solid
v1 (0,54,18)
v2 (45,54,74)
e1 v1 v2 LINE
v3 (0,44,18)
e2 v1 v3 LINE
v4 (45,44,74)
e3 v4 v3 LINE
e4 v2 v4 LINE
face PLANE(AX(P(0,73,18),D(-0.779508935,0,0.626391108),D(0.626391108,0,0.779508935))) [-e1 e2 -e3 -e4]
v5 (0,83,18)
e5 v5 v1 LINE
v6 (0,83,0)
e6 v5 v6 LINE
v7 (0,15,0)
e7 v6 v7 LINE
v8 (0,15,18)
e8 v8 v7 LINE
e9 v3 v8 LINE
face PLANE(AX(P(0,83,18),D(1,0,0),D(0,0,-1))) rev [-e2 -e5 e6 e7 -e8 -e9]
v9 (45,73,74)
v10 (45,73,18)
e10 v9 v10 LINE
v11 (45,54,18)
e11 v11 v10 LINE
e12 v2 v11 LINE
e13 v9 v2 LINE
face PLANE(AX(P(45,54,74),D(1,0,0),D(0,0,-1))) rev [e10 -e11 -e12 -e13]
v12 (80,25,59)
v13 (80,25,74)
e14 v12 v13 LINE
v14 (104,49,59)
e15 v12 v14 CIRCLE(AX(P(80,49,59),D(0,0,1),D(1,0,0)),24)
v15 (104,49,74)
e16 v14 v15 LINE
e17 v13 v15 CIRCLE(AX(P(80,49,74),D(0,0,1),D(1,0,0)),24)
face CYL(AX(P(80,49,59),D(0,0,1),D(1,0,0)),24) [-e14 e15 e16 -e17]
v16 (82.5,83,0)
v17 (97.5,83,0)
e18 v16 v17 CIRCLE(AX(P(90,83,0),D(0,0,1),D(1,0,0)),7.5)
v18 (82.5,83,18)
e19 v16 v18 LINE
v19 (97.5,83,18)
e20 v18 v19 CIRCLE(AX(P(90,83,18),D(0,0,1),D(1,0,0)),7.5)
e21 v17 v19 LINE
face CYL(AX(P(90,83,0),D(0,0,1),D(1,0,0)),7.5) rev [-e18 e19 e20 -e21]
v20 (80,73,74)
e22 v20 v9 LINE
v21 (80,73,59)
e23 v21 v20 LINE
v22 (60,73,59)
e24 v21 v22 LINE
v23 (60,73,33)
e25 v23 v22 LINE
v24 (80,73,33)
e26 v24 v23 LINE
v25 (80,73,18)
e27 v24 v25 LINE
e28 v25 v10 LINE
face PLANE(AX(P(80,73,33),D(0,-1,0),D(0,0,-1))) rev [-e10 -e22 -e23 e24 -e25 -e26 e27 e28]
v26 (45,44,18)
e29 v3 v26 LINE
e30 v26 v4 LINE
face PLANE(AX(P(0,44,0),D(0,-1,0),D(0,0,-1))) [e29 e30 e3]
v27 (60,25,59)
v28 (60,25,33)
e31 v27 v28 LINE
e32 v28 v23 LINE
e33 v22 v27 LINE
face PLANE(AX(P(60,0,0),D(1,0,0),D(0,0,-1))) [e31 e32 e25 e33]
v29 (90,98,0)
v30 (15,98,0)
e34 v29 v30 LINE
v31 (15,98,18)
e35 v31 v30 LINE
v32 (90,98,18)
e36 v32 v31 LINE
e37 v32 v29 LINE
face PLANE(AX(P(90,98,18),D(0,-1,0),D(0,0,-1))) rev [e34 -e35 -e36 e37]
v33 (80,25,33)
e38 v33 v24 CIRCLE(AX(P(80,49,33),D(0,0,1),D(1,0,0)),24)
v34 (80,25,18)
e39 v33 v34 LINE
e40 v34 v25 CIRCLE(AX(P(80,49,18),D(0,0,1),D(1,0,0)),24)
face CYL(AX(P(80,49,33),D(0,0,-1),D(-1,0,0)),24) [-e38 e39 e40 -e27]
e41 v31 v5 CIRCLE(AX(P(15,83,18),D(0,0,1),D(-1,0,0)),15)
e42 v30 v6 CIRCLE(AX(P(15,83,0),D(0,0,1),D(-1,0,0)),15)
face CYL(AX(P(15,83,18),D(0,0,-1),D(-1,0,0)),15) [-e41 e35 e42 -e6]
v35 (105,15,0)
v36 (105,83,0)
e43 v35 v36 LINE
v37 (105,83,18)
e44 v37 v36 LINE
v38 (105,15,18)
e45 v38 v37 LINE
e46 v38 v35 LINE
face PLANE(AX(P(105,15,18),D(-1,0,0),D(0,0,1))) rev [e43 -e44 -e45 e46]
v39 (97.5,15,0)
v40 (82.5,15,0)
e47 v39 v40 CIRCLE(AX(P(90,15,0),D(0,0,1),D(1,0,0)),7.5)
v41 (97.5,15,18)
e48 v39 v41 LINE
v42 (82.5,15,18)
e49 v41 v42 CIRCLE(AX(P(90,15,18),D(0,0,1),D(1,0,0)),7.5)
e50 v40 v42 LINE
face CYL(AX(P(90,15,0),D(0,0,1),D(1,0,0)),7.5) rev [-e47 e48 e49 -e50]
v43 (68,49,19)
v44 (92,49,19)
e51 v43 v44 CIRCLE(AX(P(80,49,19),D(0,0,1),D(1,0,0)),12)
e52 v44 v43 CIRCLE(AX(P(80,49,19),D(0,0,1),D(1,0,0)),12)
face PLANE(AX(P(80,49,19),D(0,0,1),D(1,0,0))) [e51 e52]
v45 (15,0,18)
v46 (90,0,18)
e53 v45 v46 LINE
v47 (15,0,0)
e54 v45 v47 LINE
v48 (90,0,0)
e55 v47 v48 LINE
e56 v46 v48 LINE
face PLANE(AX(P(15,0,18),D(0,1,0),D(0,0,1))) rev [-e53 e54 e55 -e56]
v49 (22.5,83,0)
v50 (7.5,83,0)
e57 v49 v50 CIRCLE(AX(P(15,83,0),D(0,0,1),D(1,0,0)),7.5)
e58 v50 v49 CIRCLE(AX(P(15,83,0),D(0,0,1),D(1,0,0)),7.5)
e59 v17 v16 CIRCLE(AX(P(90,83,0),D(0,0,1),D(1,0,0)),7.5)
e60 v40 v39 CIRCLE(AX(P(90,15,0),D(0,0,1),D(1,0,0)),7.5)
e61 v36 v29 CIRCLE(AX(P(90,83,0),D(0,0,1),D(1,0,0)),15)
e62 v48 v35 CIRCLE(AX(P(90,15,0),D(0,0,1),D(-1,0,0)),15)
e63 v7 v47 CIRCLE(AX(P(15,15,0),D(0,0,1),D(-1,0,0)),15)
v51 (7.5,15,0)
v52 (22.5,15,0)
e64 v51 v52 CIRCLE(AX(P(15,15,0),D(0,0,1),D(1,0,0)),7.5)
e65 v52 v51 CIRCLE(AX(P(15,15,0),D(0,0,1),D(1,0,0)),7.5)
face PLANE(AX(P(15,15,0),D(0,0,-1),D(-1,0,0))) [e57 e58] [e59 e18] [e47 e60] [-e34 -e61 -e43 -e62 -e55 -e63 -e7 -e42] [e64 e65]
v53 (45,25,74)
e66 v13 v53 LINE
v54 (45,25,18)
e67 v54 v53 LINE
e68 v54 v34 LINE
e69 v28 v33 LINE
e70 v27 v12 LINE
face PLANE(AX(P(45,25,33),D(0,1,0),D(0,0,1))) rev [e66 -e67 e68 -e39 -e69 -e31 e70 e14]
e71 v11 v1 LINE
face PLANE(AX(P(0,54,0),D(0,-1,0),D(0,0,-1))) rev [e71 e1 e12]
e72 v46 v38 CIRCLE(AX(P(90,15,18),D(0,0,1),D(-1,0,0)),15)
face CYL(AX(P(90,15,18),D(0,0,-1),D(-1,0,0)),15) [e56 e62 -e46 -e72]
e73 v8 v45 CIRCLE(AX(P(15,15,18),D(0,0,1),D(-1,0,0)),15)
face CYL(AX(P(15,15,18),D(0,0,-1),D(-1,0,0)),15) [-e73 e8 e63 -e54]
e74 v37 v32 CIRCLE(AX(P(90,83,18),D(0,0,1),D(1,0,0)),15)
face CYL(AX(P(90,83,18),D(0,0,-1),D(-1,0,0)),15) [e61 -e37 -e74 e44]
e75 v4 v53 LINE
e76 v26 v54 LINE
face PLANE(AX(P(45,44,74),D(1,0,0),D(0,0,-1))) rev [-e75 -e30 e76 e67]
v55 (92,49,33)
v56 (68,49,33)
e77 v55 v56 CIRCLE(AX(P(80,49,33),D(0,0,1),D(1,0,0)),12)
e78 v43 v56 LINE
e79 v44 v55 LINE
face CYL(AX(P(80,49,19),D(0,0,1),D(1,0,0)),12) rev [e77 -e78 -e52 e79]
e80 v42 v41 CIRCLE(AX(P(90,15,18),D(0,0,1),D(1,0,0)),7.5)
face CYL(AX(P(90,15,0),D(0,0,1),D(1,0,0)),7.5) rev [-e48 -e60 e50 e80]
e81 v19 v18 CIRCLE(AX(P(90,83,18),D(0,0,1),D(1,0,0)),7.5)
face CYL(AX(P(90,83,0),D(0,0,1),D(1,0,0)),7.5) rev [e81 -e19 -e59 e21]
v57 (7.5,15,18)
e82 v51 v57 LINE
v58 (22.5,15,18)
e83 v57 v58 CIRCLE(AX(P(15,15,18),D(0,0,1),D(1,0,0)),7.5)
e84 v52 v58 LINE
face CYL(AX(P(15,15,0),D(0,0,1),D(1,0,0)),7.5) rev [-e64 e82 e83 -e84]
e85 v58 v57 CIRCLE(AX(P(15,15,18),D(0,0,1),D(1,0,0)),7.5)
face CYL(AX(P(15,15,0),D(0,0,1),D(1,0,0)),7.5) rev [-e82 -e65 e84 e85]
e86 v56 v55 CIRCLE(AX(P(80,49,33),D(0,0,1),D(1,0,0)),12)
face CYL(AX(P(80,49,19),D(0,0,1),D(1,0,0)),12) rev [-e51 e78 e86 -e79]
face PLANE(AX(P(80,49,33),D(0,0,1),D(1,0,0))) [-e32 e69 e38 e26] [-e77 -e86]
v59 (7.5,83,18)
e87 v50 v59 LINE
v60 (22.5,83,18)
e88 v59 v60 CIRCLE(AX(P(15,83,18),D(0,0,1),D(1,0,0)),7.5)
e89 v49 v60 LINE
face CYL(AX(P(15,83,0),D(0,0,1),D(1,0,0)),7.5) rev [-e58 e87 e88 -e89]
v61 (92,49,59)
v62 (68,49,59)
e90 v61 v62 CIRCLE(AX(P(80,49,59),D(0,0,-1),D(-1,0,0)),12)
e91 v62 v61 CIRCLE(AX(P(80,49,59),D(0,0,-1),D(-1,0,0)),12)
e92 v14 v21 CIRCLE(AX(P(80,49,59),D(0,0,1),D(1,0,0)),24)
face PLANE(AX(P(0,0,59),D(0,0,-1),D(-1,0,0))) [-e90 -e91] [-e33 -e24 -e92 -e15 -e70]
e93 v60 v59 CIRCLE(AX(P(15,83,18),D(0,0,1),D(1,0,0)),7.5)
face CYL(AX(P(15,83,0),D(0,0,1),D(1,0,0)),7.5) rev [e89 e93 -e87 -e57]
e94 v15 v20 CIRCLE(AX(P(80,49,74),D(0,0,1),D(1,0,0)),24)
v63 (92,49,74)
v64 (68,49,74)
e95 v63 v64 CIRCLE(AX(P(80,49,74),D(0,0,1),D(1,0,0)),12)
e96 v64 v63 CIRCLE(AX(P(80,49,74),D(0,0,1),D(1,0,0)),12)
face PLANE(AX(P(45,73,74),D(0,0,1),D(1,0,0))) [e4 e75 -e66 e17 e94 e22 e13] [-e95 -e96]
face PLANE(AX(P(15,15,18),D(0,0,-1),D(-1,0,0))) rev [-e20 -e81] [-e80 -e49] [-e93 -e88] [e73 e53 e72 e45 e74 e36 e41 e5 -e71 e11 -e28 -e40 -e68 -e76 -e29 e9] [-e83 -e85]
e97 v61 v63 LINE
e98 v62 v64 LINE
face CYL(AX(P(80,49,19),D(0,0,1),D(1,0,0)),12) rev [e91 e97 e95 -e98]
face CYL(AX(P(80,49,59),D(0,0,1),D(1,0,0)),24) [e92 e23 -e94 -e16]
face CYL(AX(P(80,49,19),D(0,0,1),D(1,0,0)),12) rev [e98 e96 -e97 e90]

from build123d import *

# Parameters (mm, degrees)
BASE_PLATE_DEPTH           = 18
MOUNTING_HOLES_SKETCH_R    = 7.5
MOUNTING_HOLES_4X_15_DEPTH = 18
CLEVIS_BASE_BOSS_DEPTH     = 15
CLEVIS_BODY_SKETCH_W       = 10
CLEVIS_BODY_SKETCH_H       = 41
CLEVIS_BODY_DEPTH          = 48
EYE_SPACER_SKETCH_W        = 41
EYE_SPACER_SKETCH_H        = 48
EYE_SPACER_DEPTH           = 5
EYE_LUG_SKETCH_W           = 20
EYE_LUG_SKETCH_H           = 48
EYE_LUG_DEPTH              = 15
EYE_START                  = -15
EYE_LUG_ROUND_END_DEPTH    = 15
EYE_BORE_SKETCH_R          = 12
EYE_BORE_24_DEPTH          = 55
GUSSET_DEPTH               = 48
GUSSET_TRIM_A_DEPTH        = 19
GUSSET_TRIM_B_DEPTH        = 19


with BuildPart() as part:
    # Base Plate Sketch → Base Plate (new body)
    with BuildSketch(Plane.XY):
        with BuildLine():
            Line((15, 0), (90, 0))
            ThreePointArc((90, 0), (100.606601718, 4.393398282), (105, 15))
            Line((105, 15), (105, 83))
            ThreePointArc((105, 83), (100.606601718, 93.606601718), (90, 98))
            Line((90, 98), (15, 98))
            ThreePointArc((15, 98), (4.393398282, 93.606601718), (0, 83))
            Line((0, 83), (0, 15))
            ThreePointArc((0, 15), (4.393398282, 4.393398282), (15, 0))
        make_face()
    extrude(amount=BASE_PLATE_DEPTH)

    # Mounting Holes Sketch → Mounting Holes 4xØ15 (cut)
    with BuildSketch(Plane.XY.offset(18)):
        with Locations((15, 83)):
            Circle(MOUNTING_HOLES_SKETCH_R)
        with Locations((90, 83)):
            Circle(MOUNTING_HOLES_SKETCH_R)
        with Locations((90, 15)):
            Circle(MOUNTING_HOLES_SKETCH_R)
        with Locations((15, 15)):
            Circle(MOUNTING_HOLES_SKETCH_R)
    extrude(amount=-MOUNTING_HOLES_4X_15_DEPTH, mode=Mode.SUBTRACT)

    # Clevis Base Boss Sketch → Clevis Base Boss (add)
    with BuildSketch(Plane.XY.offset(18)):
        with BuildLine():
            Line((80, 73), (45, 73))
            Line((45, 73), (45, 25))
            Line((45, 25), (80, 25))
            ThreePointArc((80, 25), (104, 49), (80, 73))
        make_face()
    extrude(amount=CLEVIS_BASE_BOSS_DEPTH)

    # Clevis Body Sketch → Clevis Body (add)
    with BuildSketch(Plane.XZ.offset(-25)):
        with Locations((50, 53.5)):
            Rectangle(CLEVIS_BODY_SKETCH_W, CLEVIS_BODY_SKETCH_H)
    extrude(amount=-CLEVIS_BODY_DEPTH)

    # Eye Spacer Sketch → Eye Spacer (add)
    with BuildSketch(Plane(origin=(55, 0, 0), x_dir=(0, 0, -1), z_dir=(1, 0, 0))):
        with Locations((-53.5, 49)):
            Rectangle(EYE_SPACER_SKETCH_W, EYE_SPACER_SKETCH_H)
    extrude(amount=EYE_SPACER_DEPTH)

    # Eye Lug Sketch → Eye Lug (add)
    with BuildSketch(Plane.XY.offset(74)):
        with Locations((70, 49)):
            Rectangle(EYE_LUG_SKETCH_W, EYE_LUG_SKETCH_H)
    extrude(amount=-EYE_LUG_DEPTH)

    # Eye Lug Round End Sketch → Eye Lug Round End (add)
    with BuildSketch(Plane.XY.offset(74).offset(EYE_START)):
        with BuildLine():
            Line((80, 73), (80, 25))
            ThreePointArc((80, 25), (104, 49), (80, 73))
        make_face()
    extrude(amount=EYE_LUG_ROUND_END_DEPTH)

    # Eye Bore Sketch → Eye Bore Ø24 (cut)
    with BuildSketch(Plane.XY.offset(74)):
        with Locations((80, 49)):
            Circle(EYE_BORE_SKETCH_R)
    extrude(amount=-EYE_BORE_24_DEPTH, mode=Mode.SUBTRACT)

    # Gusset Sketch → Gusset (add)
    with BuildSketch(Plane.XZ.offset(-25)):
        Polygon((45, 74), (45, 18), (0, 18), align=None)
    extrude(amount=-GUSSET_DEPTH)

    # Gusset Trim A Sketch → Gusset Trim A (cut)
    with BuildSketch(Plane.XZ.offset(-25)):
        Polygon((45, 74), (45, 18), (0, 18), align=None)
    extrude(amount=-GUSSET_TRIM_A_DEPTH, mode=Mode.SUBTRACT)

    # Gusset Trim B Sketch → Gusset Trim B (cut)
    with BuildSketch(Plane(origin=(0, 73, 0), x_dir=(1, 0, 0), z_dir=(0, 1, 0))):
        Polygon((45, -74), (45, -18), (0, -18), align=None)
    extrude(amount=-GUSSET_TRIM_B_DEPTH, mode=Mode.SUBTRACT)


solid = part.part
